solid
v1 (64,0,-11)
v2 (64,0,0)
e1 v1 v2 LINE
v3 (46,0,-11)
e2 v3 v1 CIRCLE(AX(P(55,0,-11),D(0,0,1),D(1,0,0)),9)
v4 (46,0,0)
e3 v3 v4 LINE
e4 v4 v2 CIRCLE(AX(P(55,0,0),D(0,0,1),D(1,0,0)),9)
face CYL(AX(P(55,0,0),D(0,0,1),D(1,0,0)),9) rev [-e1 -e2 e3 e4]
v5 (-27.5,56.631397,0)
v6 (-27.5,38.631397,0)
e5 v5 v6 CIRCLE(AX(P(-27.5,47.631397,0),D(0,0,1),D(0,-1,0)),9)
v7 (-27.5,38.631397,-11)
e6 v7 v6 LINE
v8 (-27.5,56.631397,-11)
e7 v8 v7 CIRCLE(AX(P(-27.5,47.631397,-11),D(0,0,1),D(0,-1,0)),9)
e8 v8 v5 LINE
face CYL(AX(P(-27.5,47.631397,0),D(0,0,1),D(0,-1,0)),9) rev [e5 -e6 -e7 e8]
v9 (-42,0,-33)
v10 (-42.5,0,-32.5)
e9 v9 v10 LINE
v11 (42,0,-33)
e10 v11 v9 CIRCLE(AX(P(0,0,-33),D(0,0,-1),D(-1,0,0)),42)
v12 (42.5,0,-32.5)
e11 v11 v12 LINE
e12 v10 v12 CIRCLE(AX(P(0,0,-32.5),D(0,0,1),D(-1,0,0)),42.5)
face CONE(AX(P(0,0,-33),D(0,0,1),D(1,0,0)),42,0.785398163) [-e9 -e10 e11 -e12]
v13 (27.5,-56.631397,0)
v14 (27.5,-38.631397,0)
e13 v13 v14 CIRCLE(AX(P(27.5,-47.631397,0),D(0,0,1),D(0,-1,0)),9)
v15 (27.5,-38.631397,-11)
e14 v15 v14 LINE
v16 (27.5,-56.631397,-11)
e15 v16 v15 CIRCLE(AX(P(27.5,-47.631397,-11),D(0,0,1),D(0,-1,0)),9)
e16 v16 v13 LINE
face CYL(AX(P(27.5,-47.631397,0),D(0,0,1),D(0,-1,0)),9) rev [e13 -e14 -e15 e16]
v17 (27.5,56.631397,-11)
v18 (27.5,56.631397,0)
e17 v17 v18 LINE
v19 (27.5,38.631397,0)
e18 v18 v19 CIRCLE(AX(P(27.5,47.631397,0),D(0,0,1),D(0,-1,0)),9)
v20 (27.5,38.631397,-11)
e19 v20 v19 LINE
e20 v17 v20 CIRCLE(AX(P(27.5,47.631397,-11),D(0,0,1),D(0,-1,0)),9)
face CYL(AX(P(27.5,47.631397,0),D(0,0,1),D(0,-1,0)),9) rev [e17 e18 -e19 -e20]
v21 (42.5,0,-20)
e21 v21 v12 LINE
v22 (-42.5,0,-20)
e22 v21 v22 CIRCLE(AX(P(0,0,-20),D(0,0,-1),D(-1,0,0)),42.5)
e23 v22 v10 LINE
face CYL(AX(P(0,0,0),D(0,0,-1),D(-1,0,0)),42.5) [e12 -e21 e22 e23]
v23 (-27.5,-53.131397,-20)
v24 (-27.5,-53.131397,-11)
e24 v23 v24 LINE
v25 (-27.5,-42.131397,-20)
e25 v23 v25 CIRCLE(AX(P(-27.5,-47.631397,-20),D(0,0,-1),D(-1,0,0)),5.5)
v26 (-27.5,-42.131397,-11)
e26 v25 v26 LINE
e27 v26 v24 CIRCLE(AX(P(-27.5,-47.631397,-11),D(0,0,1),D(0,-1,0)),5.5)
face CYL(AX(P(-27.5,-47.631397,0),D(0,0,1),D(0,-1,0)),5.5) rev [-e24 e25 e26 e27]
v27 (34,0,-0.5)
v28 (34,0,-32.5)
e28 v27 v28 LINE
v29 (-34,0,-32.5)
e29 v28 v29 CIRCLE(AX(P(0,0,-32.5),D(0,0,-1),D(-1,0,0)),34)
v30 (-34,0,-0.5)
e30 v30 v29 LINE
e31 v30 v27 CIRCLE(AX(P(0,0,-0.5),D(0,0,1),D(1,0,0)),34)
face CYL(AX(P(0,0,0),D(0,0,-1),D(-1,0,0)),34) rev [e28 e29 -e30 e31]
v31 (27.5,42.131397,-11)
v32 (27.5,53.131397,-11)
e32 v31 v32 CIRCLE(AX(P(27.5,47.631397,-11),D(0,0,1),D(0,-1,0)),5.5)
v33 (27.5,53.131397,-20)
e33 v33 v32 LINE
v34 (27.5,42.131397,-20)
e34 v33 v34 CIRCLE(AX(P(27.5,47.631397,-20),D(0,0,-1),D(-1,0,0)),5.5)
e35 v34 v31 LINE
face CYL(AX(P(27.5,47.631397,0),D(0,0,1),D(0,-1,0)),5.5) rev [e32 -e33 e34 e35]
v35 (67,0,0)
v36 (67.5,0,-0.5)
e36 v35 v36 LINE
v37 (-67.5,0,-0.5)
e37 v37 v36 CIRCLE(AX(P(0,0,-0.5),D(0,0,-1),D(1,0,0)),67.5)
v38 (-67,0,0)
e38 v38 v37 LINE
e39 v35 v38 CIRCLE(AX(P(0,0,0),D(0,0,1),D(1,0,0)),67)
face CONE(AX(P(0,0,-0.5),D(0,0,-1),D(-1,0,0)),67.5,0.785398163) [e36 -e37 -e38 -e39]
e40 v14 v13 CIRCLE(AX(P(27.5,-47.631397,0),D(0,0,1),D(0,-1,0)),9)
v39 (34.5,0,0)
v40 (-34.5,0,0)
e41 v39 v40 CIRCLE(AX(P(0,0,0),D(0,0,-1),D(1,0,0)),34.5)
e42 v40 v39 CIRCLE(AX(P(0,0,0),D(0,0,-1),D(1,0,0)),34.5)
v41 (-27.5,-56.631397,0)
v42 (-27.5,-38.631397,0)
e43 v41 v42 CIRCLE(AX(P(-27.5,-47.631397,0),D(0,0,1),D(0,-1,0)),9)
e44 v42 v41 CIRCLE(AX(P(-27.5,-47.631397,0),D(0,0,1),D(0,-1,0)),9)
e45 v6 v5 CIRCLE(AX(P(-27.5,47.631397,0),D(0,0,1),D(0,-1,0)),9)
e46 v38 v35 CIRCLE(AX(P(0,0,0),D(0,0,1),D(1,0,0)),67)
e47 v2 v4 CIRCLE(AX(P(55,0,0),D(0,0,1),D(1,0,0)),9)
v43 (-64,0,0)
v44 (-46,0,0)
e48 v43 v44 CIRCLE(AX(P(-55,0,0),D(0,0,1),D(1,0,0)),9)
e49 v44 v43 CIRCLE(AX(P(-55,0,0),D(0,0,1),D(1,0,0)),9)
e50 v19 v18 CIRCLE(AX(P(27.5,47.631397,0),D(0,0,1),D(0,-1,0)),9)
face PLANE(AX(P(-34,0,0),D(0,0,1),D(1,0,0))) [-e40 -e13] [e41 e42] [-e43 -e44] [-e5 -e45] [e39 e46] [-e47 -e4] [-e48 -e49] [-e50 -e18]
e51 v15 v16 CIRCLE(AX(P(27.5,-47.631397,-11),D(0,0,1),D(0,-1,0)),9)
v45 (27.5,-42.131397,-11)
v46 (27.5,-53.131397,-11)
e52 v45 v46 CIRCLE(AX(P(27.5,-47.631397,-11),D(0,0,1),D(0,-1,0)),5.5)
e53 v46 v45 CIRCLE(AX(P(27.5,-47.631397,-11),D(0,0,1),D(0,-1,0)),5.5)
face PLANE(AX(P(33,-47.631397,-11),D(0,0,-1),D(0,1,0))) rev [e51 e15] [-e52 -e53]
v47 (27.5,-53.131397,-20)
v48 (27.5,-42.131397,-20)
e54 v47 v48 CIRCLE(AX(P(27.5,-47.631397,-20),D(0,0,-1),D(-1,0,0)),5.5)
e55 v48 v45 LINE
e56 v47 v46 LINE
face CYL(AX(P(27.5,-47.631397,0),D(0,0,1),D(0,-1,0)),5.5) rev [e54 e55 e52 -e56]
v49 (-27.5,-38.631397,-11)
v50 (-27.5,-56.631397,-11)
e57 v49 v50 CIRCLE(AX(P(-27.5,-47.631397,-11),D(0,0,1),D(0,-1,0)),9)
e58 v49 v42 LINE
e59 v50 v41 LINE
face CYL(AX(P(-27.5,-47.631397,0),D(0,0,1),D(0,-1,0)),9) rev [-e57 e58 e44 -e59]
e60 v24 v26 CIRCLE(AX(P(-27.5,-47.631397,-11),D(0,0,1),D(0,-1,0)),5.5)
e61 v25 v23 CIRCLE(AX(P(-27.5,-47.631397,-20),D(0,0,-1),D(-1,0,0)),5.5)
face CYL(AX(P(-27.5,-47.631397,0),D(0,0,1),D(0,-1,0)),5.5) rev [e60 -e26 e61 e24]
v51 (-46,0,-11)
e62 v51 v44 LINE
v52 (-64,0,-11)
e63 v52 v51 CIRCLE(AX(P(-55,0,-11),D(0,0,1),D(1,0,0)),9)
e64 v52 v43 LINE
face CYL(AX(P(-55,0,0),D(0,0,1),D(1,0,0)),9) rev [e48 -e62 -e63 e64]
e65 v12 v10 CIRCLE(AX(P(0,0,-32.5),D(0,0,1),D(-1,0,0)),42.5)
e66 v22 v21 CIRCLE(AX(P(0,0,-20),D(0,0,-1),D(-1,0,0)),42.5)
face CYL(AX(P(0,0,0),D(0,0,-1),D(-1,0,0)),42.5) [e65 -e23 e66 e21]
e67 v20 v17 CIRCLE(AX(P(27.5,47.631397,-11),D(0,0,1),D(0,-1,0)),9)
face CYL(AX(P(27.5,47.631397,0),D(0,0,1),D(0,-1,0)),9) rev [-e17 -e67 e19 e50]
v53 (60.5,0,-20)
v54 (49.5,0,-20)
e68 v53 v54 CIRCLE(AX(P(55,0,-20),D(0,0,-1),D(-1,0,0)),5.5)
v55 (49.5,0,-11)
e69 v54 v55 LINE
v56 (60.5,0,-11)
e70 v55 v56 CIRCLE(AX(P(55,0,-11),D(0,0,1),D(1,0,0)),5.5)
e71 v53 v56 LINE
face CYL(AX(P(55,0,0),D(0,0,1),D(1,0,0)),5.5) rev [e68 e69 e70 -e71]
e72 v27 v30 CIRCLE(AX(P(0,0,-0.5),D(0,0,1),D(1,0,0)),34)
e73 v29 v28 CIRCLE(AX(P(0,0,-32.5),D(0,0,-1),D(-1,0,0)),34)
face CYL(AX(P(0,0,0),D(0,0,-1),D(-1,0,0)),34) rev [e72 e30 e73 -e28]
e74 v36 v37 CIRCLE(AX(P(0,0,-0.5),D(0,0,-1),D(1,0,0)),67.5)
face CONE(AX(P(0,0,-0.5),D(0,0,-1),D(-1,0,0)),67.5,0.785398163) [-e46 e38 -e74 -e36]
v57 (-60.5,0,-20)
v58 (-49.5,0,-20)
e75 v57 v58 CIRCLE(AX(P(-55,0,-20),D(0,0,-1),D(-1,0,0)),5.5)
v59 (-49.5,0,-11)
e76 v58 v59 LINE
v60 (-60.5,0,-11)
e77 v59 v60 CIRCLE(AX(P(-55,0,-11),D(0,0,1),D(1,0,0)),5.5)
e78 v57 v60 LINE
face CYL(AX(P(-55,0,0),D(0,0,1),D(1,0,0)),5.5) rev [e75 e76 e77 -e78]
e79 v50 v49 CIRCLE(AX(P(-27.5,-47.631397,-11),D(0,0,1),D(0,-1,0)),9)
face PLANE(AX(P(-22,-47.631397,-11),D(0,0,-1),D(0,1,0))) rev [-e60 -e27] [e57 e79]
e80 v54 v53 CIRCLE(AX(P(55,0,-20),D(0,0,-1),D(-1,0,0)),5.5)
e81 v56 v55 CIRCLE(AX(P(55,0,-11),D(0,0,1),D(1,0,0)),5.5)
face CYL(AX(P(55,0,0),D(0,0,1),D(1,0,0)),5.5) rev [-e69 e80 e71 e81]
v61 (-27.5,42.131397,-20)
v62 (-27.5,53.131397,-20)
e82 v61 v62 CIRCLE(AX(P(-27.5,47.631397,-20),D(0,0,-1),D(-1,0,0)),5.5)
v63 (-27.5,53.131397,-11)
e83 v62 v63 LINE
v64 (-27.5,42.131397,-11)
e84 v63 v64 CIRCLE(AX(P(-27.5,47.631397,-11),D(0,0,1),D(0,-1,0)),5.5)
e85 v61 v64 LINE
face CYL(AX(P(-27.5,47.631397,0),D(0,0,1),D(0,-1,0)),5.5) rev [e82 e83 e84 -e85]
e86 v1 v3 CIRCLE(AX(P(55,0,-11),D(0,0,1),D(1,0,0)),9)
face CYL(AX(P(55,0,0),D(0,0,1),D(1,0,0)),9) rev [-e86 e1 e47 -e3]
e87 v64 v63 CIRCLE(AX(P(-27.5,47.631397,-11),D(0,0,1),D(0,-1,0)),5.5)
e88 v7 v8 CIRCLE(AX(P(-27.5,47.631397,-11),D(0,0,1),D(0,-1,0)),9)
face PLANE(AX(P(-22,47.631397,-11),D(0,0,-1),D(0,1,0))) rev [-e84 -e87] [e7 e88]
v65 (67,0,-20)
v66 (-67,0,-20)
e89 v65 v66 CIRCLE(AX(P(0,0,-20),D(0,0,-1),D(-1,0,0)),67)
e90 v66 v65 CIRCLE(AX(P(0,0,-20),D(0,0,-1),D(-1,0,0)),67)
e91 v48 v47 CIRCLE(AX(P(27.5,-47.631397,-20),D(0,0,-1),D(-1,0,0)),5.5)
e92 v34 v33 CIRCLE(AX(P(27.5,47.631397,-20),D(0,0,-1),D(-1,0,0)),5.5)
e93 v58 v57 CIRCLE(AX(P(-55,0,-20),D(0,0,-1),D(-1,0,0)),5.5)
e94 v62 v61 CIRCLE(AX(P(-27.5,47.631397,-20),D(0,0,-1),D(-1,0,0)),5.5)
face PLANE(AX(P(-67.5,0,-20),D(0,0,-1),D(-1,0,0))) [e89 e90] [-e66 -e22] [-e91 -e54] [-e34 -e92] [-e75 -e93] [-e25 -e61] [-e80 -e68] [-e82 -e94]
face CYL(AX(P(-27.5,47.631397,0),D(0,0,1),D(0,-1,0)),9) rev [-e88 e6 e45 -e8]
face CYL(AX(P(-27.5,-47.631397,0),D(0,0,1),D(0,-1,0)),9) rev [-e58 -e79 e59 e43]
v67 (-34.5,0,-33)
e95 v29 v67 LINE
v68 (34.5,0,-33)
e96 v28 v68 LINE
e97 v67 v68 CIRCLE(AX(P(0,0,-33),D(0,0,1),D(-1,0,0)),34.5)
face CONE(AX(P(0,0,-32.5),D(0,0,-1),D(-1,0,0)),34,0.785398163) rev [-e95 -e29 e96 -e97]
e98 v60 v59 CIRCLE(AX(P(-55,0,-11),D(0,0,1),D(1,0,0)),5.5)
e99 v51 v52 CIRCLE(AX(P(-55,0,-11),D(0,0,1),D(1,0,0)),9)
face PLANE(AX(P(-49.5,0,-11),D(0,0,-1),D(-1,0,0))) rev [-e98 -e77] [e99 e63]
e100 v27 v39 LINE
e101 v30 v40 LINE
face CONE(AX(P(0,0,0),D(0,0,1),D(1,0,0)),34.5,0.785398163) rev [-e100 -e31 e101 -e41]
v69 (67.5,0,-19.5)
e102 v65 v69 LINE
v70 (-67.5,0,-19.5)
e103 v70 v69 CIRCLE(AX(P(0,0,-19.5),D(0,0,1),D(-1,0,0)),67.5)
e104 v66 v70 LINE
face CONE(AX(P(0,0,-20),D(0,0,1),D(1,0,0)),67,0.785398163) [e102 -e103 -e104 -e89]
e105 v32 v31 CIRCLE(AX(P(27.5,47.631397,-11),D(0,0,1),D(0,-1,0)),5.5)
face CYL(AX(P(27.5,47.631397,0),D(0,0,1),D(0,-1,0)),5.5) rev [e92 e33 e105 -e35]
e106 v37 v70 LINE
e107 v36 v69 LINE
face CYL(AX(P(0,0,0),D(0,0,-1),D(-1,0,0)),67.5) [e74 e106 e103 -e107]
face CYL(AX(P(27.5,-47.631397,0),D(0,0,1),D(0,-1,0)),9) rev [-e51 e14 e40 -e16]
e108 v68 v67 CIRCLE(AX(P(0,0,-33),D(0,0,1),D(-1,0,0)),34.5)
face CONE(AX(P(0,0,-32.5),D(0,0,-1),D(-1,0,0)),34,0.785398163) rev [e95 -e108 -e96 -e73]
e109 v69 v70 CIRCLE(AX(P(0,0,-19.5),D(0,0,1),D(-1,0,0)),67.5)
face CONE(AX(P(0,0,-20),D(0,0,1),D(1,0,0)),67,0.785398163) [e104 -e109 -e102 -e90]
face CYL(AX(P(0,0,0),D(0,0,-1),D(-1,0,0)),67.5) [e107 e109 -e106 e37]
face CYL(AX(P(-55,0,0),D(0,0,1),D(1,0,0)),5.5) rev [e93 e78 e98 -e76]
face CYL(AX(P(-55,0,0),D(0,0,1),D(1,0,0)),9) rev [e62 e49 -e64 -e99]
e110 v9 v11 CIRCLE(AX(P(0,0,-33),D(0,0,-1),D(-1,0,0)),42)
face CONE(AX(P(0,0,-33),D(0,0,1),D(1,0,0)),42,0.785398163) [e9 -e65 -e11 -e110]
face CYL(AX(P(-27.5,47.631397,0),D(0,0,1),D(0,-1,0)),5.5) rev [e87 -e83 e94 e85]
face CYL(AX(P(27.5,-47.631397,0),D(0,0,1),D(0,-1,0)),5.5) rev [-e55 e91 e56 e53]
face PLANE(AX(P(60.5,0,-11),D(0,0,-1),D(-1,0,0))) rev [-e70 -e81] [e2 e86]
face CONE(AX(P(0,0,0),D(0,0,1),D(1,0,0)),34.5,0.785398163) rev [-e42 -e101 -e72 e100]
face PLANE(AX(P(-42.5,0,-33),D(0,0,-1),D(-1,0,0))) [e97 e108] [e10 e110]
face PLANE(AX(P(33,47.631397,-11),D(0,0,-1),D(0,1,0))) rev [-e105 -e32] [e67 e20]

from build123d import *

# Parameters (mm, degrees)
HOLE_WIZARD_1_D           = 11
HOLE_WIZARD_1_CBORE_D     = 18
HOLE_WIZARD_1_CBORE_DEPTH = 11
PATTERN_CIRCULAR_1_COUNT  = 6
CHAMFER_1_SIZE            = 0.5


with BuildPart() as part:
    # 草图1 → 旋转1 (revolve)
    with BuildSketch(Plane(origin=(0, 0, 0), x_dir=(1, 0, 0), z_dir=(0, 1, 0))):
        Polygon((-34, 0), (-67.5, 0), (-67.5, 20), (-42.5, 20), (-42.5, 33), (-34, 33), align=None)
    revolve(axis=Axis((0, 0, 0), (0, 0, 1)))

    # 打孔尺寸(%根据)内六角圆柱头螺钉的类型1 (through all)
    with Locations(Plane.XY):
        with Locations((55, 0)):
            hole_wizard_1 = CounterBoreHole(HOLE_WIZARD_1_D / 2, HOLE_WIZARD_1_CBORE_D / 2, HOLE_WIZARD_1_CBORE_DEPTH)

    # 阵列(圆周)1: 打孔尺寸(%根据)内六角圆柱头螺钉的类型1 ×6 about axis
    pattern_circular_1_axis = Axis((0, 0, 0), (0, 0, 1))
    for i in range(1, PATTERN_CIRCULAR_1_COUNT):
        add(hole_wizard_1.rotate(pattern_circular_1_axis, i * 360 / PATTERN_CIRCULAR_1_COUNT), mode=Mode.SUBTRACT)

    # 倒角1
    chamfer_1_edges = [part.edges().sort_by_distance(p)[0] for p in [
        (67.5, 0, 0),
        (34, 0, 0),
        (34, 0, -33),
        (42.5, 0, -33),
        (67.5, 0, -20),
    ]]
    chamfer(chamfer_1_edges, length=CHAMFER_1_SIZE)


solid = part.part
